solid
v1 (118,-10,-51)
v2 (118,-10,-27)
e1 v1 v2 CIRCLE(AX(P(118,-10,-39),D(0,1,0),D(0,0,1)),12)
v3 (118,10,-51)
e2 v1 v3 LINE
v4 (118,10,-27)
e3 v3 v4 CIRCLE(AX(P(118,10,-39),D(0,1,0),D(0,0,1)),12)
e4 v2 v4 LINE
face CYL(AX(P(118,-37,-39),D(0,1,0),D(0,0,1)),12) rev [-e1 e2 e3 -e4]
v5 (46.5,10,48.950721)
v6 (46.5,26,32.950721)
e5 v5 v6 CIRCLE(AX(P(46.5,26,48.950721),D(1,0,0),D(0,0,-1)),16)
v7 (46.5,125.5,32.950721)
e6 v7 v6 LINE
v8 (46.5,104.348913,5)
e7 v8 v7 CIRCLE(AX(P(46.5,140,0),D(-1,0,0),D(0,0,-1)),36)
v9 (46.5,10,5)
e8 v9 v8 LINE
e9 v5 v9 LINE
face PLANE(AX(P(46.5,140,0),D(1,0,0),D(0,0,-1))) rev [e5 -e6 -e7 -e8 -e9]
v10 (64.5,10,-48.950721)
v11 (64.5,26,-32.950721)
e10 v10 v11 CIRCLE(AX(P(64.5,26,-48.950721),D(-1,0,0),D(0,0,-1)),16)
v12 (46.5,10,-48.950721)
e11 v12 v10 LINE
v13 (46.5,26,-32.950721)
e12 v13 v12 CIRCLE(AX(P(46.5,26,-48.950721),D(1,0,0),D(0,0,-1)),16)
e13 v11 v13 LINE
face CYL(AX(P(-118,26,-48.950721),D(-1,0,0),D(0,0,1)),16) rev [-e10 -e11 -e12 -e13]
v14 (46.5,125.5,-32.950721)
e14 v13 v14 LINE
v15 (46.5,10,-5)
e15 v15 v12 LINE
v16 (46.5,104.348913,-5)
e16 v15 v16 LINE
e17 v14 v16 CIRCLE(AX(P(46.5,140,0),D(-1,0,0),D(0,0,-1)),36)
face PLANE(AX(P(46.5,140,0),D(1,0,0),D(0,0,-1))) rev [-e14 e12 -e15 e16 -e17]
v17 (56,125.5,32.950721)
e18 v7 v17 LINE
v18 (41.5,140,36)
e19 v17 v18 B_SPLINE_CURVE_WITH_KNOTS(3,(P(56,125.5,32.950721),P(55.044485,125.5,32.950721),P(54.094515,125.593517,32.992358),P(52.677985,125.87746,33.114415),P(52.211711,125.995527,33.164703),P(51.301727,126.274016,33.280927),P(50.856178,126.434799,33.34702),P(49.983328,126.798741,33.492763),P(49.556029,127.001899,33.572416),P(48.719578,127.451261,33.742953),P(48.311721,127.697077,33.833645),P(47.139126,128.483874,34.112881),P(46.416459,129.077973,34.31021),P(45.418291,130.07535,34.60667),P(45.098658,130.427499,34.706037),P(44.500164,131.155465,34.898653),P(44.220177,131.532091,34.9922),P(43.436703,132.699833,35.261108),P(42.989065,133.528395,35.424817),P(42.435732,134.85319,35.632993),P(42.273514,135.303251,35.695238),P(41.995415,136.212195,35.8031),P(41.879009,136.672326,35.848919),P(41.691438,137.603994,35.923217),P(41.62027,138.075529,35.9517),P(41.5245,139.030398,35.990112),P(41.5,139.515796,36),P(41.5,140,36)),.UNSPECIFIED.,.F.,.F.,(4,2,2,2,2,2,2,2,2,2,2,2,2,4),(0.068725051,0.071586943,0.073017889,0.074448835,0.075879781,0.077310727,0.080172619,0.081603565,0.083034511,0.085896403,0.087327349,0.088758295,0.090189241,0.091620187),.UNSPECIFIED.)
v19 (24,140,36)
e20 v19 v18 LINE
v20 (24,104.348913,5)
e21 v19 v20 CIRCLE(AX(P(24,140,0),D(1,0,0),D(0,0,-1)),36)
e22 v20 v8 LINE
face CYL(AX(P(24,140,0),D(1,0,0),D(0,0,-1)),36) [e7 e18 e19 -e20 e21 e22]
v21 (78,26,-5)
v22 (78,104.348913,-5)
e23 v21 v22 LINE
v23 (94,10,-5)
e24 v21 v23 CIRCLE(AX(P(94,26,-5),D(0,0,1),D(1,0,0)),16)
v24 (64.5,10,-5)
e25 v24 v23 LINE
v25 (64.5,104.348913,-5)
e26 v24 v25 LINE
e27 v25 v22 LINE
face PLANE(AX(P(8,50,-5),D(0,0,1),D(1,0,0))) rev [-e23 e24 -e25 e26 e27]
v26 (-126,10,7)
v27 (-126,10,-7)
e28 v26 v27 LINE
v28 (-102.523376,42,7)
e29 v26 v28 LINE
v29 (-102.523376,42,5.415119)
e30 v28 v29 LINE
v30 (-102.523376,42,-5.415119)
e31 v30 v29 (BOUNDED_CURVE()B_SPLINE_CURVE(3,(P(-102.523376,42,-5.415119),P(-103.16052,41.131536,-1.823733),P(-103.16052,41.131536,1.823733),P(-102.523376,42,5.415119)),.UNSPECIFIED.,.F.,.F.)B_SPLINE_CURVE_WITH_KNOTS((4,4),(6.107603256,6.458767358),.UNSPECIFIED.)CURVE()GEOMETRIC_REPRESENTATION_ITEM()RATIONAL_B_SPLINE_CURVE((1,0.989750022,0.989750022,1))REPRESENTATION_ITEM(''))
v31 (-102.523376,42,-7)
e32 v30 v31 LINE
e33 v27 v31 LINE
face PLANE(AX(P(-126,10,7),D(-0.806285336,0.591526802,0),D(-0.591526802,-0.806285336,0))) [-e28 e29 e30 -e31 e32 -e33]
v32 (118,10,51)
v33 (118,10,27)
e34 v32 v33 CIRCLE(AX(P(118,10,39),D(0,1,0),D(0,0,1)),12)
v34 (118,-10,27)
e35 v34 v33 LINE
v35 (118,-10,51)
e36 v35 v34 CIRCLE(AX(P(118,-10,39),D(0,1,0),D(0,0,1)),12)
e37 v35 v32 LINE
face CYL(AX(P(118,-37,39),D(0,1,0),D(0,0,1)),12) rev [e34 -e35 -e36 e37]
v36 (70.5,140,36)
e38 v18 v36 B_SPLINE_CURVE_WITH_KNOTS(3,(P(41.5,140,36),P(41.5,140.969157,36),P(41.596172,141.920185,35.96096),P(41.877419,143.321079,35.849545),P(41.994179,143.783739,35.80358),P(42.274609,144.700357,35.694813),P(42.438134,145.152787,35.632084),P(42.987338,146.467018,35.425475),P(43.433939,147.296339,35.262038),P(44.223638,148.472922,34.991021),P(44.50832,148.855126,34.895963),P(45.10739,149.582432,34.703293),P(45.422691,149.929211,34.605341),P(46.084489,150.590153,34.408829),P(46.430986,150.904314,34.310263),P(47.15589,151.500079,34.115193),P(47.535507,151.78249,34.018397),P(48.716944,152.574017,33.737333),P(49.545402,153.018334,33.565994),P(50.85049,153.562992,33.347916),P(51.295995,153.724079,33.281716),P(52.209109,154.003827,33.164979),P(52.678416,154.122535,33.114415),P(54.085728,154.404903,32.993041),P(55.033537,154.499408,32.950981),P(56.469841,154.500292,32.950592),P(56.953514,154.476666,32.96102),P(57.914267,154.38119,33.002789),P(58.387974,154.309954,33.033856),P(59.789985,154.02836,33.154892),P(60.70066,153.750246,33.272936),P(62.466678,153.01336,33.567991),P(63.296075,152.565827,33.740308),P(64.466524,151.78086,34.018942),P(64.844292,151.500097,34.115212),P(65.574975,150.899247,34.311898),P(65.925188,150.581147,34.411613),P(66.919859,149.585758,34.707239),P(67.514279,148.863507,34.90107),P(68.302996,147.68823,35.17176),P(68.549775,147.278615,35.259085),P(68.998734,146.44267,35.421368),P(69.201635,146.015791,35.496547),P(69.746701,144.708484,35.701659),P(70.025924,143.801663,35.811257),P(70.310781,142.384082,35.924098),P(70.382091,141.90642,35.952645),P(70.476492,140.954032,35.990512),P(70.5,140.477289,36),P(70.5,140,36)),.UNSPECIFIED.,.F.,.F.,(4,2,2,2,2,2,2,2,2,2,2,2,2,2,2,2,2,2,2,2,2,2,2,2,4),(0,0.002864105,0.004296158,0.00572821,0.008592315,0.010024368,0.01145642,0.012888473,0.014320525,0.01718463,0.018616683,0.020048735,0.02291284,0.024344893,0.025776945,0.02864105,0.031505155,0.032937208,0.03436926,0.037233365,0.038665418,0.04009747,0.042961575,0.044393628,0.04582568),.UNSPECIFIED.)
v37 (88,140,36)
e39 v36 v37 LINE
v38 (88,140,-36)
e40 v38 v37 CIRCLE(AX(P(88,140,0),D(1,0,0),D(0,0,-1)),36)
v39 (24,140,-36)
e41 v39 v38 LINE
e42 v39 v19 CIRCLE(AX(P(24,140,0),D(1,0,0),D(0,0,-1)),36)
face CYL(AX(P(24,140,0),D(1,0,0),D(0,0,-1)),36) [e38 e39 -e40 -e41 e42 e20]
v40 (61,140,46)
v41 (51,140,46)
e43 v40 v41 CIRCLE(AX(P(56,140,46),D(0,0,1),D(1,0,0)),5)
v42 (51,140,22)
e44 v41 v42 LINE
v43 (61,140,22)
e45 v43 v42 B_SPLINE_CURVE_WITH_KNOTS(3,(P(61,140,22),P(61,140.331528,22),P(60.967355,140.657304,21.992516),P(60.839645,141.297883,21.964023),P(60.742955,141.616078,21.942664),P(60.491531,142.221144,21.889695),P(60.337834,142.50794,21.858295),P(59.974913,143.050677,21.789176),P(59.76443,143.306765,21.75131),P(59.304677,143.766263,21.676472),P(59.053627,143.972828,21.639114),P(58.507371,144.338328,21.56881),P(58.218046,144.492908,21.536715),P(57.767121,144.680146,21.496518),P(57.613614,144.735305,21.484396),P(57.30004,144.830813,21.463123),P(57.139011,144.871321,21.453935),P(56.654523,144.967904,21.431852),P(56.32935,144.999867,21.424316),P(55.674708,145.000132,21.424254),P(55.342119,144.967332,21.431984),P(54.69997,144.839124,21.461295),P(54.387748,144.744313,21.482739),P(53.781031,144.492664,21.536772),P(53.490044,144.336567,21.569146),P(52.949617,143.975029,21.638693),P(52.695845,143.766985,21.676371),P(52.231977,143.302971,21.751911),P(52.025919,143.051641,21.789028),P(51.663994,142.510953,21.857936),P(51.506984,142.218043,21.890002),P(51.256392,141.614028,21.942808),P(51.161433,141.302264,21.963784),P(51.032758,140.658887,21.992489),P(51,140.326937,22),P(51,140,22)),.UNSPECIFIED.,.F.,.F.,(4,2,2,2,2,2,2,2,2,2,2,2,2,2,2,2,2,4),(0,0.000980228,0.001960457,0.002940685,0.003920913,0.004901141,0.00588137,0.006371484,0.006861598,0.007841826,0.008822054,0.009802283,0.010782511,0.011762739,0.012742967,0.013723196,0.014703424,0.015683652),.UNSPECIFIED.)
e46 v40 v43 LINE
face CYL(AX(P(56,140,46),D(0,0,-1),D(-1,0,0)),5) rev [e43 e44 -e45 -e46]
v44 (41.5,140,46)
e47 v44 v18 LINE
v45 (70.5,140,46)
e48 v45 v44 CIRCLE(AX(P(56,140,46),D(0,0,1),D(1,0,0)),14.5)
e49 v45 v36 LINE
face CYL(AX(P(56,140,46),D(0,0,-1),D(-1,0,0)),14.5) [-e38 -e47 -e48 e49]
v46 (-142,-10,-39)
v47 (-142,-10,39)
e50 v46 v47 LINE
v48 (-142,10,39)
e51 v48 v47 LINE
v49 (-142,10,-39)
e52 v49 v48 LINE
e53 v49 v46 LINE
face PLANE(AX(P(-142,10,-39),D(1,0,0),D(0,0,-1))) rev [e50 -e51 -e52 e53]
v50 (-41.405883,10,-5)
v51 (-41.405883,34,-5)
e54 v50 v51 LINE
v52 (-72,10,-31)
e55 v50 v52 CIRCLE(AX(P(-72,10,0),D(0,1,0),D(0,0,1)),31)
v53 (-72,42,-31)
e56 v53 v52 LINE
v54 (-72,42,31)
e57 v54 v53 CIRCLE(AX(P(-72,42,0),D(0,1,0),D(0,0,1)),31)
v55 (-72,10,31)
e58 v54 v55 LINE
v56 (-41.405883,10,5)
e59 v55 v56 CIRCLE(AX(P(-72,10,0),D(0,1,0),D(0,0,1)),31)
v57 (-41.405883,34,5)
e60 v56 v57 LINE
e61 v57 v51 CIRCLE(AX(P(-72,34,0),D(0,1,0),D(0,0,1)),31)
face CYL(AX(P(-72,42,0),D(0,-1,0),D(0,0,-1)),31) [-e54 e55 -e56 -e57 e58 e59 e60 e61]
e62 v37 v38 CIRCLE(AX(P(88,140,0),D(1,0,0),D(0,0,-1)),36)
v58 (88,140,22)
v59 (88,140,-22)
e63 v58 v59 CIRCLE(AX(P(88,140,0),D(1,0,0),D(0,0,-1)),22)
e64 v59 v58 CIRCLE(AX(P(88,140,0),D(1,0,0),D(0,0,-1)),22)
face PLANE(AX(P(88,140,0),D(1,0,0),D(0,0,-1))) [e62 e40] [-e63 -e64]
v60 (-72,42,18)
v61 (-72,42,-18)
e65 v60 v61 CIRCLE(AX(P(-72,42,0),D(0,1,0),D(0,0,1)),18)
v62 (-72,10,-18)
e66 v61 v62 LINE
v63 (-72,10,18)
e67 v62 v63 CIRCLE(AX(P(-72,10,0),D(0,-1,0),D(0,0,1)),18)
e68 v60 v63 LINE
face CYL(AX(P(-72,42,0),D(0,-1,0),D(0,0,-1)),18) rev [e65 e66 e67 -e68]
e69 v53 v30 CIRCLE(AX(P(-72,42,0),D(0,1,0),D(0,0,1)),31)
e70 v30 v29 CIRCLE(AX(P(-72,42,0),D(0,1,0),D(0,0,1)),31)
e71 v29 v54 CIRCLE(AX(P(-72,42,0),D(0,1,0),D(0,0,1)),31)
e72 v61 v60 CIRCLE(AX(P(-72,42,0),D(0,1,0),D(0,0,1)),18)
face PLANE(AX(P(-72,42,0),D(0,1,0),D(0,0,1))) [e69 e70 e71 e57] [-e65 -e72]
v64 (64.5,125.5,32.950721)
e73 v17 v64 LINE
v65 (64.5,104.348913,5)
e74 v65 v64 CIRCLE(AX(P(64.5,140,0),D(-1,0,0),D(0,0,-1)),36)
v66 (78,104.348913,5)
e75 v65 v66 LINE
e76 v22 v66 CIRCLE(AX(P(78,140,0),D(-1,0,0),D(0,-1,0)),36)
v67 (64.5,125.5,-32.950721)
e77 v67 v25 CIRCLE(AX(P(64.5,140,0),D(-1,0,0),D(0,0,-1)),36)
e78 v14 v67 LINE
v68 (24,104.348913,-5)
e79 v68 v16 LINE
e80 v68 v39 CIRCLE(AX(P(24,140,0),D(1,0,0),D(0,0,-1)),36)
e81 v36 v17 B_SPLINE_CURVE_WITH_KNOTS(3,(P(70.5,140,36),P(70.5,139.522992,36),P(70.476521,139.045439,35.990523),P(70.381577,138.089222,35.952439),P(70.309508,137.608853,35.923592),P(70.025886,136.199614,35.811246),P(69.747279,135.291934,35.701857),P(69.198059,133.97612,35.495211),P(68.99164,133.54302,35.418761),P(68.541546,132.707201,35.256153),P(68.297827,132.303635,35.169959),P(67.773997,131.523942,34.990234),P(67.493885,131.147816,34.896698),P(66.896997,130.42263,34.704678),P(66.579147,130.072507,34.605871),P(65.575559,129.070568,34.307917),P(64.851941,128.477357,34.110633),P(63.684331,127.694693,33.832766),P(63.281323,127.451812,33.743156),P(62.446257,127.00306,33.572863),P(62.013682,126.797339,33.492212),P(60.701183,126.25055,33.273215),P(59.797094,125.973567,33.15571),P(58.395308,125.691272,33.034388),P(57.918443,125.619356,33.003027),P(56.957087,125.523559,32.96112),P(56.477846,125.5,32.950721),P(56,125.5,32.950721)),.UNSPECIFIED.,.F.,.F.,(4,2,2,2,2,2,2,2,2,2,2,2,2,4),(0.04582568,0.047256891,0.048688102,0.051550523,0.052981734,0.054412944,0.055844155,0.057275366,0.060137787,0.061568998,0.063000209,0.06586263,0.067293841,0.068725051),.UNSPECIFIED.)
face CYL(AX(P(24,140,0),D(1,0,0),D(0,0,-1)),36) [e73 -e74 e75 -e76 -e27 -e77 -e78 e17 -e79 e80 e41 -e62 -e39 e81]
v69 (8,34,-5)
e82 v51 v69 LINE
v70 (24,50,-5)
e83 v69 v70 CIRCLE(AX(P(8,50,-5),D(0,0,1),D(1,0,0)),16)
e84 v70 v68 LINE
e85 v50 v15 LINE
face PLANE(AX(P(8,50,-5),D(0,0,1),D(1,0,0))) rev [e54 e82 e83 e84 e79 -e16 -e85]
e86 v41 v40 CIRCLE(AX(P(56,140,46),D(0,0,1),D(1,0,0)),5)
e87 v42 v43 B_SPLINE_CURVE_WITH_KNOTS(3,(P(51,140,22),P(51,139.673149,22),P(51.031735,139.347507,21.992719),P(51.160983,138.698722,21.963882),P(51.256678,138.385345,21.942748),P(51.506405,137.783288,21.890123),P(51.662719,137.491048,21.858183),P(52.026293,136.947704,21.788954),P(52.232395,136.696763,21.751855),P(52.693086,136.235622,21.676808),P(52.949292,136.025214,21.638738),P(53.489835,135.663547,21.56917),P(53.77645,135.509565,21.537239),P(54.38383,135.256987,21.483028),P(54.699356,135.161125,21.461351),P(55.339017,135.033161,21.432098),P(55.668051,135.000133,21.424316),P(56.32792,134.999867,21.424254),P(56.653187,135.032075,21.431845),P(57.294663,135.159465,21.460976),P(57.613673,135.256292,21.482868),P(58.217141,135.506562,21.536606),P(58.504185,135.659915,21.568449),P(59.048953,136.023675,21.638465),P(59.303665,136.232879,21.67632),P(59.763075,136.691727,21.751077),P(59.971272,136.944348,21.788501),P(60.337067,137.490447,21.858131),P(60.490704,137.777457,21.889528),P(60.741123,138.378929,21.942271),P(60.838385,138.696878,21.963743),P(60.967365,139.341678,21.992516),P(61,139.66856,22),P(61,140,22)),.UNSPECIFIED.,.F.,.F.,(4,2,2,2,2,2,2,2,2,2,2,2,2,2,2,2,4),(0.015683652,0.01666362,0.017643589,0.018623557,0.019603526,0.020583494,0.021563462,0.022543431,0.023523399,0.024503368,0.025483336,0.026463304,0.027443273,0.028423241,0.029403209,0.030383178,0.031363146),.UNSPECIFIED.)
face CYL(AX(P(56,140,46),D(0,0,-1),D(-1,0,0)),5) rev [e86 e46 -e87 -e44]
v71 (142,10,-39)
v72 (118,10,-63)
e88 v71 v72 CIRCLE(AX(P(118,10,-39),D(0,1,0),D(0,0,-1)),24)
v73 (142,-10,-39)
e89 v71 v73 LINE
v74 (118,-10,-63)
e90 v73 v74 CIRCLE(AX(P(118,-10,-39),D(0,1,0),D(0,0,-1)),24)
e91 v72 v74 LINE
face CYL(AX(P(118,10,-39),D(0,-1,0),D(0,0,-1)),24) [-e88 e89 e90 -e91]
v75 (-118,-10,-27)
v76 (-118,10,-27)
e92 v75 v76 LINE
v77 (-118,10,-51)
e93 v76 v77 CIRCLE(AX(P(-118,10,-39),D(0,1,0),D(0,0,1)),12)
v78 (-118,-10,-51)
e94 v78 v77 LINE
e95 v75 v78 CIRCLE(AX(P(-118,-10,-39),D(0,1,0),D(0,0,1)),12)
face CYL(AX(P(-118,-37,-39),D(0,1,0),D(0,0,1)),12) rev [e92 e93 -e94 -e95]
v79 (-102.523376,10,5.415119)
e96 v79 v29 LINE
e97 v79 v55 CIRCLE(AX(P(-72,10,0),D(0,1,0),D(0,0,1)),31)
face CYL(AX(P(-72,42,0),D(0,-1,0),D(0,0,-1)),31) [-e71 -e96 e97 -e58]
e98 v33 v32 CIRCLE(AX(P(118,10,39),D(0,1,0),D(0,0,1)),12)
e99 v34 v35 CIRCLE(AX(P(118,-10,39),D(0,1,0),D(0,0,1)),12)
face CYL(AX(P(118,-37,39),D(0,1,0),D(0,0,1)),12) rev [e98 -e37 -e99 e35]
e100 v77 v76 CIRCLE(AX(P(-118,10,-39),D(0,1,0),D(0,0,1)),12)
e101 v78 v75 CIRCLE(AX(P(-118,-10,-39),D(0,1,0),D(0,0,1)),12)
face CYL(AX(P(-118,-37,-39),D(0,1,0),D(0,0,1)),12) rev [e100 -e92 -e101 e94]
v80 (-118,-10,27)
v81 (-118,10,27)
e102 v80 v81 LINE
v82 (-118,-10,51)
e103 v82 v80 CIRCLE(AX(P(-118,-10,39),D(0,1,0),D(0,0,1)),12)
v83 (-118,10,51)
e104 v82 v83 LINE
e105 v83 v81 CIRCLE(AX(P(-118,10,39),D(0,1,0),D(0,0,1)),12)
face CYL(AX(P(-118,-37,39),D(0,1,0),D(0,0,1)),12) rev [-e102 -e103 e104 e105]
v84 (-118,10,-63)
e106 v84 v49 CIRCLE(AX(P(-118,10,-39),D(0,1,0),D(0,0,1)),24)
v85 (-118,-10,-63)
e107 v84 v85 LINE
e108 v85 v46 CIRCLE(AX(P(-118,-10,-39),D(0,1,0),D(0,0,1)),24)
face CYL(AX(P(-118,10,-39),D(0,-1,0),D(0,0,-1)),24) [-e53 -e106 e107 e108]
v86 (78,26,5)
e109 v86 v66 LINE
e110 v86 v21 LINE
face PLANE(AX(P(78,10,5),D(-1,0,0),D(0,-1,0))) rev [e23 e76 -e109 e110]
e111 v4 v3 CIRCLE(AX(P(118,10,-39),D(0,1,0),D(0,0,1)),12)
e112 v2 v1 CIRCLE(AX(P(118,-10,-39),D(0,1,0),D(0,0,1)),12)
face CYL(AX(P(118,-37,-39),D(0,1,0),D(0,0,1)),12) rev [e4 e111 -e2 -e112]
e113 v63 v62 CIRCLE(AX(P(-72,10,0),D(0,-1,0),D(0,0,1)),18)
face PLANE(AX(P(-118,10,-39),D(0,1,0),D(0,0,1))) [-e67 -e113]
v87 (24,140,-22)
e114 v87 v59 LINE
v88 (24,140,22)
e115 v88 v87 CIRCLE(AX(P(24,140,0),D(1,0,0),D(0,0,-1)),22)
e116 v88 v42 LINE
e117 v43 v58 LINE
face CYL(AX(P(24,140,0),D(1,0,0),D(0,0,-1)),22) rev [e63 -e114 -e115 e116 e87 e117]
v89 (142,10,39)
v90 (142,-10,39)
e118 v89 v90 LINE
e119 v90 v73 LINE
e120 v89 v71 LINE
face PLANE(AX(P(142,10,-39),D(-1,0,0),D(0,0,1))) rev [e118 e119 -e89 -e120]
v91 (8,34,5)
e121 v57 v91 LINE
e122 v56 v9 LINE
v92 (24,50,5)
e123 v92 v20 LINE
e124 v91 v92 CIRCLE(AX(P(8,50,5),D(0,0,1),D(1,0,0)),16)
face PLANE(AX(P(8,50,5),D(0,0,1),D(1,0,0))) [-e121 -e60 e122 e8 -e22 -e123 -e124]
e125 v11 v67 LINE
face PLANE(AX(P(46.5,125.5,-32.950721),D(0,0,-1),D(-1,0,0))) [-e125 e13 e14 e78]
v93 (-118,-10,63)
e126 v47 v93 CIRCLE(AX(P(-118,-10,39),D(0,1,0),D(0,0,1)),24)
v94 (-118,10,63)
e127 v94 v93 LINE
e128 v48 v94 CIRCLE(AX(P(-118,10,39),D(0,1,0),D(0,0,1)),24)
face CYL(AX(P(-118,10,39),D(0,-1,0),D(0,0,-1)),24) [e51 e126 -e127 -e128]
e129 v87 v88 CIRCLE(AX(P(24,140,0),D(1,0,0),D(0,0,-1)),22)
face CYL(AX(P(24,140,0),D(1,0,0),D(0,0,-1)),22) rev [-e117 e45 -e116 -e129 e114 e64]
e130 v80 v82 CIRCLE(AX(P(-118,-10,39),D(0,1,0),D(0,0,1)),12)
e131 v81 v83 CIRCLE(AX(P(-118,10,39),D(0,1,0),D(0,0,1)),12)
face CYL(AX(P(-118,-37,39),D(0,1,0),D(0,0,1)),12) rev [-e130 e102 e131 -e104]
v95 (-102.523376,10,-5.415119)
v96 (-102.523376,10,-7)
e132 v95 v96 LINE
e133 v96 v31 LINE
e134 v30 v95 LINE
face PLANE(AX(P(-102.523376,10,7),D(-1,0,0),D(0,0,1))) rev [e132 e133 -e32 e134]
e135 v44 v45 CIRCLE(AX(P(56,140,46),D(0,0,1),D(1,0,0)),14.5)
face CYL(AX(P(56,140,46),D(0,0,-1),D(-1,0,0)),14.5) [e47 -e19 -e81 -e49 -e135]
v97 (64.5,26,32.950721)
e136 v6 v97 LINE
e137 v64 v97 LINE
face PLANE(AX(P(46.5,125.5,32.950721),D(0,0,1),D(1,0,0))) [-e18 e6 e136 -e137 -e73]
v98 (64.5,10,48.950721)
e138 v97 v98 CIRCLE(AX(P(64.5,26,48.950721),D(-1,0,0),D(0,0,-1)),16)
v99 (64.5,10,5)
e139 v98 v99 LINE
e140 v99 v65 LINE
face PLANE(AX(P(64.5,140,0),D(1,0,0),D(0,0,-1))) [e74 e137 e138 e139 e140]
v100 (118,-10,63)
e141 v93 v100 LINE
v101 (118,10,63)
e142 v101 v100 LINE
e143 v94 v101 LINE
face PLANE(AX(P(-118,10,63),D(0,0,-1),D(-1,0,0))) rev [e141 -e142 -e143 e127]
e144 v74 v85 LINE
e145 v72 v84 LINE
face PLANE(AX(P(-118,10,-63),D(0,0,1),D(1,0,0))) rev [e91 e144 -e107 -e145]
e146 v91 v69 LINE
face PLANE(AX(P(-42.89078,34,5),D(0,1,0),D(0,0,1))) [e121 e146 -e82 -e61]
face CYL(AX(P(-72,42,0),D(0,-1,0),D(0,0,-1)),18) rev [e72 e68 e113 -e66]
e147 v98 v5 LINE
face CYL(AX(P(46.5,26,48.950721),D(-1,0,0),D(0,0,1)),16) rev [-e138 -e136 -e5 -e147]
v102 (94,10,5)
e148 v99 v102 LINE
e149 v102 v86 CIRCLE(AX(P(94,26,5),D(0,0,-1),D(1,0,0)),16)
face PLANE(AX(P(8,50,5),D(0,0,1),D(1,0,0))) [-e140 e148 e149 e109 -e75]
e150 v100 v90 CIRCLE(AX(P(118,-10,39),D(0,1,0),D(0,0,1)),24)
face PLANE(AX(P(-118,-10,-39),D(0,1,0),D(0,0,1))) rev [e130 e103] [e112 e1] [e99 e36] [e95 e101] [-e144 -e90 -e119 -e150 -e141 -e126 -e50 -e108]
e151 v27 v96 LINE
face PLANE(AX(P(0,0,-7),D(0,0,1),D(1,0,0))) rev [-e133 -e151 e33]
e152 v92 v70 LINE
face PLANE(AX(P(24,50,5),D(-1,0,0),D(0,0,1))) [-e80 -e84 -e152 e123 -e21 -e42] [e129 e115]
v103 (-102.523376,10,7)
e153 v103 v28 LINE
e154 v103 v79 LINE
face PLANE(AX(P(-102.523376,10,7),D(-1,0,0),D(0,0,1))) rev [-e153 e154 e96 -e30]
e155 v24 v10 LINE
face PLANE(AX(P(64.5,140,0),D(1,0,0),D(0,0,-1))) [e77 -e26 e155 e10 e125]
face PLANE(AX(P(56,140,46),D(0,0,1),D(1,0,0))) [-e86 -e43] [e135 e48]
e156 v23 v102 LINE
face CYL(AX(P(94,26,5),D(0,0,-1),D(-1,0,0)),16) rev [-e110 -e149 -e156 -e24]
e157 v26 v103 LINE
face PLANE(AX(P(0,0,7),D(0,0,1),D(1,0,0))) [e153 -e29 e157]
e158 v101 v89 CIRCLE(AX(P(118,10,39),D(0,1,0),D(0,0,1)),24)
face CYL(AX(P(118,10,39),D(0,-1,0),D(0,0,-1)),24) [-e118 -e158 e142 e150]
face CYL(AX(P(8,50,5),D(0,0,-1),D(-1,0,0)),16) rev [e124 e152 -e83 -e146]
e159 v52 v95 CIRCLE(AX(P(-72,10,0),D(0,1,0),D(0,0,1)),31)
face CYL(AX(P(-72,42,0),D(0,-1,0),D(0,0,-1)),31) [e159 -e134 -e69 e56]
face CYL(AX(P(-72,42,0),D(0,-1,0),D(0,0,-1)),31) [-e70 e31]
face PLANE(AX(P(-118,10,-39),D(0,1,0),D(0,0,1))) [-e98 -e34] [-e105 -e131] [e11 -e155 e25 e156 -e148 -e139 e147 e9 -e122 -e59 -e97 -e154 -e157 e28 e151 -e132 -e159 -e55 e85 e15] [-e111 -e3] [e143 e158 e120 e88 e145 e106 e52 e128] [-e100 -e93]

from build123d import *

# Parameters (mm, degrees)
BASE_PLATE_DEPTH           = 10
PLATE_BOSS_SKETCH_R        = 31
PLATE_BOSS_SKETCH_R_2      = 18
PLATE_BOSS_DEPTH           = 32
CONNECTING_RIB_DEPTH       = 7
BEARING_HOUSING_SKETCH_R   = 36
BEARING_HOUSING_SKETCH_R_2 = 22
BEARING_HOUSING_DEPTH      = 64
SUPPORT_WEB_DEPTH          = 5
PIN_LUG_SKETCH_R           = 14.5
PIN_LUG_SKETCH_R_2         = 5
PIN_LUG_DEPTH              = 46
SIDE_START                 = -13.5
SIDE_RIBS_DEPTH            = 18
SIDE_RIB_FILLETS_R16_R     = 16
WEB_SLOT_SKETCH_R          = 12
WEB_SLOT_DEPTH             = 47
HOUSING_BORE_SKETCH_R      = 22
HOUSING_BORE_DEPTH         = 47
LUG_START                  = -47
LUG_PIN_HOLE_SKETCH_R      = 5
LUG_PIN_HOLE_DEPTH         = 47
WEB_BASE_FILLETS_R16_R     = 16


with BuildPart() as part:
    # Base Plate Sketch → Base Plate (new, symmetric)
    with BuildSketch(Plane(origin=(0, 0, 0), x_dir=(1, 0, 0), z_dir=(0, 1, 0))):
        with BuildLine():
            Line((-118, 63), (118, 63))
            ThreePointArc((118, 63), (134.970562748, 55.970562748), (142, 39))
            Line((142, 39), (142, -39))
            ThreePointArc((142, -39), (134.970562748, -55.970562748), (118, -63))
            Line((118, -63), (-118, -63))
            ThreePointArc((-118, -63), (-134.970562748, -55.970562748), (-142, -39))
            Line((-142, -39), (-142, 39))
            ThreePointArc((-142, 39), (-134.970562748, 55.970562748), (-118, 63))
        make_face()
    extrude(amount=BASE_PLATE_DEPTH, both=True)

    # Plate Boss Sketch → Plate Boss (add)
    with BuildSketch(Plane(origin=(0, 10, 0), x_dir=(1, 0, 0), z_dir=(0, 1, 0))):
        with Locations(Location((-72, 0, 0), (0, 0, 270))):
            Circle(PLATE_BOSS_SKETCH_R)
        with Locations(Location((-72, 0, 0), (0, 0, 270))):
            Circle(PLATE_BOSS_SKETCH_R_2, mode=Mode.SUBTRACT)
    extrude(amount=PLATE_BOSS_DEPTH)

    # Connecting Rib Sketch → Connecting Rib (add, symmetric)
    with BuildSketch(Plane.XY):
        Polygon((-126, 10), (-102.523376003, 42), (-102.523376003, 10), align=None)
    extrude(amount=CONNECTING_RIB_DEPTH, both=True)



with BuildPart() as body_2:
    # Bearing Housing Sketch → Bearing Housing (new body)
    with BuildSketch(Plane(origin=(88, 0, 0), x_dir=(0, 0, -1), z_dir=(1, 0, 0))):
        with Locations((0, 140)):
            Circle(BEARING_HOUSING_SKETCH_R)
        with Locations((0, 140)):
            Circle(BEARING_HOUSING_SKETCH_R_2, mode=Mode.SUBTRACT)
    extrude(amount=-BEARING_HOUSING_DEPTH)


with BuildPart() as part_1:
    add(part.part)

    add(body_2.part)  # Support Web merges body 2
    # Support Web Sketch → Support Web (add, symmetric)
    with BuildSketch(Plane.XY):
        with BuildLine():
            Line((-42.890780427, 10), (-42.890780427, 34))
            Line((-42.890780427, 34), (8, 34))
            ThreePointArc((8, 34), (19.313708499, 38.686291501), (24, 50))
            Line((24, 50), (24, 106.55673196))
            Line((24, 106.55673196), (78, 106.55673196))
            Line((78, 106.55673196), (78, 10))
            Line((78, 10), (-42.890780427, 10))
        make_face()
    extrude(amount=SUPPORT_WEB_DEPTH, both=True)

    # Pin Lug Sketch → Pin Lug (add)
    with BuildSketch(Plane.XY):
        with Locations(Location((56, 140, 0), (0, 0, 180))):
            Circle(PIN_LUG_SKETCH_R)
        with Locations(Location((56, 140, 0), (0, 0, 180))):
            Circle(PIN_LUG_SKETCH_R_2, mode=Mode.SUBTRACT)
    extrude(amount=PIN_LUG_DEPTH)

    # Side Ribs Sketch → Side Ribs (add)
    with BuildSketch(Plane(origin=(78, 0, 0), x_dir=(0, 0, -1), z_dir=(1, 0, 0)).offset(SIDE_START)):
        with BuildLine():
            Line((-32.950720781, 125.5), (-32.950720781, 10))
            Line((-32.950720781, 10), (32.950720781, 10))
            Line((32.950720781, 10), (32.950720781, 125.5))
            ThreePointArc((32.950720781, 125.5), (0, 104), (-32.950720781, 125.5))
        make_face()
    extrude(amount=-SIDE_RIBS_DEPTH)

    # Side Rib Fillets R16
    side_rib_fillets_r16_edges = [part_1.edges().sort_by_distance(p)[0] for p in [
        (55.5, 10, -32.950720781),
        (55.5, 10, 32.950720781),
    ]]
    fillet(side_rib_fillets_r16_edges, radius=SIDE_RIB_FILLETS_R16_R)

    # Web Slot Sketch → Web Slot (cut)
    with BuildSketch(Plane(origin=(0, 10, 0), x_dir=(1, 0, 0), z_dir=(0, 1, 0))):
        with Locations(Location((-118, 39, 0), (0, 0, 270))):
            Circle(WEB_SLOT_SKETCH_R)
        with Locations(Location((-118, -39, 0), (0, 0, 270))):
            Circle(WEB_SLOT_SKETCH_R)
        with Locations(Location((118, -39, 0), (0, 0, 270))):
            Circle(WEB_SLOT_SKETCH_R)
        with Locations(Location((118, 39, 0), (0, 0, 270))):
            Circle(WEB_SLOT_SKETCH_R)
    extrude(amount=-WEB_SLOT_DEPTH, mode=Mode.SUBTRACT)

    # Housing Bore Sketch → Housing Bore (cut)
    with BuildSketch(Plane(origin=(88, 0, 0), x_dir=(0, 0, -1), z_dir=(1, 0, 0))):
        with Locations((0, 140)):
            Circle(HOUSING_BORE_SKETCH_R)
    extrude(amount=-HOUSING_BORE_DEPTH, mode=Mode.SUBTRACT)

    # Lug Pin Hole Sketch → Lug Pin Hole (cut)
    with BuildSketch(Plane.XY.offset(46).offset(LUG_START)):
        with Locations((56, 140)):
            Circle(LUG_PIN_HOLE_SKETCH_R)
    extrude(amount=LUG_PIN_HOLE_DEPTH, mode=Mode.SUBTRACT)

    # Web Base Fillets R16
    web_base_fillets_r16_edges = [part_1.edges().sort_by_distance(p)[0] for p in [
        (78, 10, 0),
    ]]
    fillet(web_base_fillets_r16_edges, radius=WEB_BASE_FILLETS_R16_R)


solid = part_1.part
